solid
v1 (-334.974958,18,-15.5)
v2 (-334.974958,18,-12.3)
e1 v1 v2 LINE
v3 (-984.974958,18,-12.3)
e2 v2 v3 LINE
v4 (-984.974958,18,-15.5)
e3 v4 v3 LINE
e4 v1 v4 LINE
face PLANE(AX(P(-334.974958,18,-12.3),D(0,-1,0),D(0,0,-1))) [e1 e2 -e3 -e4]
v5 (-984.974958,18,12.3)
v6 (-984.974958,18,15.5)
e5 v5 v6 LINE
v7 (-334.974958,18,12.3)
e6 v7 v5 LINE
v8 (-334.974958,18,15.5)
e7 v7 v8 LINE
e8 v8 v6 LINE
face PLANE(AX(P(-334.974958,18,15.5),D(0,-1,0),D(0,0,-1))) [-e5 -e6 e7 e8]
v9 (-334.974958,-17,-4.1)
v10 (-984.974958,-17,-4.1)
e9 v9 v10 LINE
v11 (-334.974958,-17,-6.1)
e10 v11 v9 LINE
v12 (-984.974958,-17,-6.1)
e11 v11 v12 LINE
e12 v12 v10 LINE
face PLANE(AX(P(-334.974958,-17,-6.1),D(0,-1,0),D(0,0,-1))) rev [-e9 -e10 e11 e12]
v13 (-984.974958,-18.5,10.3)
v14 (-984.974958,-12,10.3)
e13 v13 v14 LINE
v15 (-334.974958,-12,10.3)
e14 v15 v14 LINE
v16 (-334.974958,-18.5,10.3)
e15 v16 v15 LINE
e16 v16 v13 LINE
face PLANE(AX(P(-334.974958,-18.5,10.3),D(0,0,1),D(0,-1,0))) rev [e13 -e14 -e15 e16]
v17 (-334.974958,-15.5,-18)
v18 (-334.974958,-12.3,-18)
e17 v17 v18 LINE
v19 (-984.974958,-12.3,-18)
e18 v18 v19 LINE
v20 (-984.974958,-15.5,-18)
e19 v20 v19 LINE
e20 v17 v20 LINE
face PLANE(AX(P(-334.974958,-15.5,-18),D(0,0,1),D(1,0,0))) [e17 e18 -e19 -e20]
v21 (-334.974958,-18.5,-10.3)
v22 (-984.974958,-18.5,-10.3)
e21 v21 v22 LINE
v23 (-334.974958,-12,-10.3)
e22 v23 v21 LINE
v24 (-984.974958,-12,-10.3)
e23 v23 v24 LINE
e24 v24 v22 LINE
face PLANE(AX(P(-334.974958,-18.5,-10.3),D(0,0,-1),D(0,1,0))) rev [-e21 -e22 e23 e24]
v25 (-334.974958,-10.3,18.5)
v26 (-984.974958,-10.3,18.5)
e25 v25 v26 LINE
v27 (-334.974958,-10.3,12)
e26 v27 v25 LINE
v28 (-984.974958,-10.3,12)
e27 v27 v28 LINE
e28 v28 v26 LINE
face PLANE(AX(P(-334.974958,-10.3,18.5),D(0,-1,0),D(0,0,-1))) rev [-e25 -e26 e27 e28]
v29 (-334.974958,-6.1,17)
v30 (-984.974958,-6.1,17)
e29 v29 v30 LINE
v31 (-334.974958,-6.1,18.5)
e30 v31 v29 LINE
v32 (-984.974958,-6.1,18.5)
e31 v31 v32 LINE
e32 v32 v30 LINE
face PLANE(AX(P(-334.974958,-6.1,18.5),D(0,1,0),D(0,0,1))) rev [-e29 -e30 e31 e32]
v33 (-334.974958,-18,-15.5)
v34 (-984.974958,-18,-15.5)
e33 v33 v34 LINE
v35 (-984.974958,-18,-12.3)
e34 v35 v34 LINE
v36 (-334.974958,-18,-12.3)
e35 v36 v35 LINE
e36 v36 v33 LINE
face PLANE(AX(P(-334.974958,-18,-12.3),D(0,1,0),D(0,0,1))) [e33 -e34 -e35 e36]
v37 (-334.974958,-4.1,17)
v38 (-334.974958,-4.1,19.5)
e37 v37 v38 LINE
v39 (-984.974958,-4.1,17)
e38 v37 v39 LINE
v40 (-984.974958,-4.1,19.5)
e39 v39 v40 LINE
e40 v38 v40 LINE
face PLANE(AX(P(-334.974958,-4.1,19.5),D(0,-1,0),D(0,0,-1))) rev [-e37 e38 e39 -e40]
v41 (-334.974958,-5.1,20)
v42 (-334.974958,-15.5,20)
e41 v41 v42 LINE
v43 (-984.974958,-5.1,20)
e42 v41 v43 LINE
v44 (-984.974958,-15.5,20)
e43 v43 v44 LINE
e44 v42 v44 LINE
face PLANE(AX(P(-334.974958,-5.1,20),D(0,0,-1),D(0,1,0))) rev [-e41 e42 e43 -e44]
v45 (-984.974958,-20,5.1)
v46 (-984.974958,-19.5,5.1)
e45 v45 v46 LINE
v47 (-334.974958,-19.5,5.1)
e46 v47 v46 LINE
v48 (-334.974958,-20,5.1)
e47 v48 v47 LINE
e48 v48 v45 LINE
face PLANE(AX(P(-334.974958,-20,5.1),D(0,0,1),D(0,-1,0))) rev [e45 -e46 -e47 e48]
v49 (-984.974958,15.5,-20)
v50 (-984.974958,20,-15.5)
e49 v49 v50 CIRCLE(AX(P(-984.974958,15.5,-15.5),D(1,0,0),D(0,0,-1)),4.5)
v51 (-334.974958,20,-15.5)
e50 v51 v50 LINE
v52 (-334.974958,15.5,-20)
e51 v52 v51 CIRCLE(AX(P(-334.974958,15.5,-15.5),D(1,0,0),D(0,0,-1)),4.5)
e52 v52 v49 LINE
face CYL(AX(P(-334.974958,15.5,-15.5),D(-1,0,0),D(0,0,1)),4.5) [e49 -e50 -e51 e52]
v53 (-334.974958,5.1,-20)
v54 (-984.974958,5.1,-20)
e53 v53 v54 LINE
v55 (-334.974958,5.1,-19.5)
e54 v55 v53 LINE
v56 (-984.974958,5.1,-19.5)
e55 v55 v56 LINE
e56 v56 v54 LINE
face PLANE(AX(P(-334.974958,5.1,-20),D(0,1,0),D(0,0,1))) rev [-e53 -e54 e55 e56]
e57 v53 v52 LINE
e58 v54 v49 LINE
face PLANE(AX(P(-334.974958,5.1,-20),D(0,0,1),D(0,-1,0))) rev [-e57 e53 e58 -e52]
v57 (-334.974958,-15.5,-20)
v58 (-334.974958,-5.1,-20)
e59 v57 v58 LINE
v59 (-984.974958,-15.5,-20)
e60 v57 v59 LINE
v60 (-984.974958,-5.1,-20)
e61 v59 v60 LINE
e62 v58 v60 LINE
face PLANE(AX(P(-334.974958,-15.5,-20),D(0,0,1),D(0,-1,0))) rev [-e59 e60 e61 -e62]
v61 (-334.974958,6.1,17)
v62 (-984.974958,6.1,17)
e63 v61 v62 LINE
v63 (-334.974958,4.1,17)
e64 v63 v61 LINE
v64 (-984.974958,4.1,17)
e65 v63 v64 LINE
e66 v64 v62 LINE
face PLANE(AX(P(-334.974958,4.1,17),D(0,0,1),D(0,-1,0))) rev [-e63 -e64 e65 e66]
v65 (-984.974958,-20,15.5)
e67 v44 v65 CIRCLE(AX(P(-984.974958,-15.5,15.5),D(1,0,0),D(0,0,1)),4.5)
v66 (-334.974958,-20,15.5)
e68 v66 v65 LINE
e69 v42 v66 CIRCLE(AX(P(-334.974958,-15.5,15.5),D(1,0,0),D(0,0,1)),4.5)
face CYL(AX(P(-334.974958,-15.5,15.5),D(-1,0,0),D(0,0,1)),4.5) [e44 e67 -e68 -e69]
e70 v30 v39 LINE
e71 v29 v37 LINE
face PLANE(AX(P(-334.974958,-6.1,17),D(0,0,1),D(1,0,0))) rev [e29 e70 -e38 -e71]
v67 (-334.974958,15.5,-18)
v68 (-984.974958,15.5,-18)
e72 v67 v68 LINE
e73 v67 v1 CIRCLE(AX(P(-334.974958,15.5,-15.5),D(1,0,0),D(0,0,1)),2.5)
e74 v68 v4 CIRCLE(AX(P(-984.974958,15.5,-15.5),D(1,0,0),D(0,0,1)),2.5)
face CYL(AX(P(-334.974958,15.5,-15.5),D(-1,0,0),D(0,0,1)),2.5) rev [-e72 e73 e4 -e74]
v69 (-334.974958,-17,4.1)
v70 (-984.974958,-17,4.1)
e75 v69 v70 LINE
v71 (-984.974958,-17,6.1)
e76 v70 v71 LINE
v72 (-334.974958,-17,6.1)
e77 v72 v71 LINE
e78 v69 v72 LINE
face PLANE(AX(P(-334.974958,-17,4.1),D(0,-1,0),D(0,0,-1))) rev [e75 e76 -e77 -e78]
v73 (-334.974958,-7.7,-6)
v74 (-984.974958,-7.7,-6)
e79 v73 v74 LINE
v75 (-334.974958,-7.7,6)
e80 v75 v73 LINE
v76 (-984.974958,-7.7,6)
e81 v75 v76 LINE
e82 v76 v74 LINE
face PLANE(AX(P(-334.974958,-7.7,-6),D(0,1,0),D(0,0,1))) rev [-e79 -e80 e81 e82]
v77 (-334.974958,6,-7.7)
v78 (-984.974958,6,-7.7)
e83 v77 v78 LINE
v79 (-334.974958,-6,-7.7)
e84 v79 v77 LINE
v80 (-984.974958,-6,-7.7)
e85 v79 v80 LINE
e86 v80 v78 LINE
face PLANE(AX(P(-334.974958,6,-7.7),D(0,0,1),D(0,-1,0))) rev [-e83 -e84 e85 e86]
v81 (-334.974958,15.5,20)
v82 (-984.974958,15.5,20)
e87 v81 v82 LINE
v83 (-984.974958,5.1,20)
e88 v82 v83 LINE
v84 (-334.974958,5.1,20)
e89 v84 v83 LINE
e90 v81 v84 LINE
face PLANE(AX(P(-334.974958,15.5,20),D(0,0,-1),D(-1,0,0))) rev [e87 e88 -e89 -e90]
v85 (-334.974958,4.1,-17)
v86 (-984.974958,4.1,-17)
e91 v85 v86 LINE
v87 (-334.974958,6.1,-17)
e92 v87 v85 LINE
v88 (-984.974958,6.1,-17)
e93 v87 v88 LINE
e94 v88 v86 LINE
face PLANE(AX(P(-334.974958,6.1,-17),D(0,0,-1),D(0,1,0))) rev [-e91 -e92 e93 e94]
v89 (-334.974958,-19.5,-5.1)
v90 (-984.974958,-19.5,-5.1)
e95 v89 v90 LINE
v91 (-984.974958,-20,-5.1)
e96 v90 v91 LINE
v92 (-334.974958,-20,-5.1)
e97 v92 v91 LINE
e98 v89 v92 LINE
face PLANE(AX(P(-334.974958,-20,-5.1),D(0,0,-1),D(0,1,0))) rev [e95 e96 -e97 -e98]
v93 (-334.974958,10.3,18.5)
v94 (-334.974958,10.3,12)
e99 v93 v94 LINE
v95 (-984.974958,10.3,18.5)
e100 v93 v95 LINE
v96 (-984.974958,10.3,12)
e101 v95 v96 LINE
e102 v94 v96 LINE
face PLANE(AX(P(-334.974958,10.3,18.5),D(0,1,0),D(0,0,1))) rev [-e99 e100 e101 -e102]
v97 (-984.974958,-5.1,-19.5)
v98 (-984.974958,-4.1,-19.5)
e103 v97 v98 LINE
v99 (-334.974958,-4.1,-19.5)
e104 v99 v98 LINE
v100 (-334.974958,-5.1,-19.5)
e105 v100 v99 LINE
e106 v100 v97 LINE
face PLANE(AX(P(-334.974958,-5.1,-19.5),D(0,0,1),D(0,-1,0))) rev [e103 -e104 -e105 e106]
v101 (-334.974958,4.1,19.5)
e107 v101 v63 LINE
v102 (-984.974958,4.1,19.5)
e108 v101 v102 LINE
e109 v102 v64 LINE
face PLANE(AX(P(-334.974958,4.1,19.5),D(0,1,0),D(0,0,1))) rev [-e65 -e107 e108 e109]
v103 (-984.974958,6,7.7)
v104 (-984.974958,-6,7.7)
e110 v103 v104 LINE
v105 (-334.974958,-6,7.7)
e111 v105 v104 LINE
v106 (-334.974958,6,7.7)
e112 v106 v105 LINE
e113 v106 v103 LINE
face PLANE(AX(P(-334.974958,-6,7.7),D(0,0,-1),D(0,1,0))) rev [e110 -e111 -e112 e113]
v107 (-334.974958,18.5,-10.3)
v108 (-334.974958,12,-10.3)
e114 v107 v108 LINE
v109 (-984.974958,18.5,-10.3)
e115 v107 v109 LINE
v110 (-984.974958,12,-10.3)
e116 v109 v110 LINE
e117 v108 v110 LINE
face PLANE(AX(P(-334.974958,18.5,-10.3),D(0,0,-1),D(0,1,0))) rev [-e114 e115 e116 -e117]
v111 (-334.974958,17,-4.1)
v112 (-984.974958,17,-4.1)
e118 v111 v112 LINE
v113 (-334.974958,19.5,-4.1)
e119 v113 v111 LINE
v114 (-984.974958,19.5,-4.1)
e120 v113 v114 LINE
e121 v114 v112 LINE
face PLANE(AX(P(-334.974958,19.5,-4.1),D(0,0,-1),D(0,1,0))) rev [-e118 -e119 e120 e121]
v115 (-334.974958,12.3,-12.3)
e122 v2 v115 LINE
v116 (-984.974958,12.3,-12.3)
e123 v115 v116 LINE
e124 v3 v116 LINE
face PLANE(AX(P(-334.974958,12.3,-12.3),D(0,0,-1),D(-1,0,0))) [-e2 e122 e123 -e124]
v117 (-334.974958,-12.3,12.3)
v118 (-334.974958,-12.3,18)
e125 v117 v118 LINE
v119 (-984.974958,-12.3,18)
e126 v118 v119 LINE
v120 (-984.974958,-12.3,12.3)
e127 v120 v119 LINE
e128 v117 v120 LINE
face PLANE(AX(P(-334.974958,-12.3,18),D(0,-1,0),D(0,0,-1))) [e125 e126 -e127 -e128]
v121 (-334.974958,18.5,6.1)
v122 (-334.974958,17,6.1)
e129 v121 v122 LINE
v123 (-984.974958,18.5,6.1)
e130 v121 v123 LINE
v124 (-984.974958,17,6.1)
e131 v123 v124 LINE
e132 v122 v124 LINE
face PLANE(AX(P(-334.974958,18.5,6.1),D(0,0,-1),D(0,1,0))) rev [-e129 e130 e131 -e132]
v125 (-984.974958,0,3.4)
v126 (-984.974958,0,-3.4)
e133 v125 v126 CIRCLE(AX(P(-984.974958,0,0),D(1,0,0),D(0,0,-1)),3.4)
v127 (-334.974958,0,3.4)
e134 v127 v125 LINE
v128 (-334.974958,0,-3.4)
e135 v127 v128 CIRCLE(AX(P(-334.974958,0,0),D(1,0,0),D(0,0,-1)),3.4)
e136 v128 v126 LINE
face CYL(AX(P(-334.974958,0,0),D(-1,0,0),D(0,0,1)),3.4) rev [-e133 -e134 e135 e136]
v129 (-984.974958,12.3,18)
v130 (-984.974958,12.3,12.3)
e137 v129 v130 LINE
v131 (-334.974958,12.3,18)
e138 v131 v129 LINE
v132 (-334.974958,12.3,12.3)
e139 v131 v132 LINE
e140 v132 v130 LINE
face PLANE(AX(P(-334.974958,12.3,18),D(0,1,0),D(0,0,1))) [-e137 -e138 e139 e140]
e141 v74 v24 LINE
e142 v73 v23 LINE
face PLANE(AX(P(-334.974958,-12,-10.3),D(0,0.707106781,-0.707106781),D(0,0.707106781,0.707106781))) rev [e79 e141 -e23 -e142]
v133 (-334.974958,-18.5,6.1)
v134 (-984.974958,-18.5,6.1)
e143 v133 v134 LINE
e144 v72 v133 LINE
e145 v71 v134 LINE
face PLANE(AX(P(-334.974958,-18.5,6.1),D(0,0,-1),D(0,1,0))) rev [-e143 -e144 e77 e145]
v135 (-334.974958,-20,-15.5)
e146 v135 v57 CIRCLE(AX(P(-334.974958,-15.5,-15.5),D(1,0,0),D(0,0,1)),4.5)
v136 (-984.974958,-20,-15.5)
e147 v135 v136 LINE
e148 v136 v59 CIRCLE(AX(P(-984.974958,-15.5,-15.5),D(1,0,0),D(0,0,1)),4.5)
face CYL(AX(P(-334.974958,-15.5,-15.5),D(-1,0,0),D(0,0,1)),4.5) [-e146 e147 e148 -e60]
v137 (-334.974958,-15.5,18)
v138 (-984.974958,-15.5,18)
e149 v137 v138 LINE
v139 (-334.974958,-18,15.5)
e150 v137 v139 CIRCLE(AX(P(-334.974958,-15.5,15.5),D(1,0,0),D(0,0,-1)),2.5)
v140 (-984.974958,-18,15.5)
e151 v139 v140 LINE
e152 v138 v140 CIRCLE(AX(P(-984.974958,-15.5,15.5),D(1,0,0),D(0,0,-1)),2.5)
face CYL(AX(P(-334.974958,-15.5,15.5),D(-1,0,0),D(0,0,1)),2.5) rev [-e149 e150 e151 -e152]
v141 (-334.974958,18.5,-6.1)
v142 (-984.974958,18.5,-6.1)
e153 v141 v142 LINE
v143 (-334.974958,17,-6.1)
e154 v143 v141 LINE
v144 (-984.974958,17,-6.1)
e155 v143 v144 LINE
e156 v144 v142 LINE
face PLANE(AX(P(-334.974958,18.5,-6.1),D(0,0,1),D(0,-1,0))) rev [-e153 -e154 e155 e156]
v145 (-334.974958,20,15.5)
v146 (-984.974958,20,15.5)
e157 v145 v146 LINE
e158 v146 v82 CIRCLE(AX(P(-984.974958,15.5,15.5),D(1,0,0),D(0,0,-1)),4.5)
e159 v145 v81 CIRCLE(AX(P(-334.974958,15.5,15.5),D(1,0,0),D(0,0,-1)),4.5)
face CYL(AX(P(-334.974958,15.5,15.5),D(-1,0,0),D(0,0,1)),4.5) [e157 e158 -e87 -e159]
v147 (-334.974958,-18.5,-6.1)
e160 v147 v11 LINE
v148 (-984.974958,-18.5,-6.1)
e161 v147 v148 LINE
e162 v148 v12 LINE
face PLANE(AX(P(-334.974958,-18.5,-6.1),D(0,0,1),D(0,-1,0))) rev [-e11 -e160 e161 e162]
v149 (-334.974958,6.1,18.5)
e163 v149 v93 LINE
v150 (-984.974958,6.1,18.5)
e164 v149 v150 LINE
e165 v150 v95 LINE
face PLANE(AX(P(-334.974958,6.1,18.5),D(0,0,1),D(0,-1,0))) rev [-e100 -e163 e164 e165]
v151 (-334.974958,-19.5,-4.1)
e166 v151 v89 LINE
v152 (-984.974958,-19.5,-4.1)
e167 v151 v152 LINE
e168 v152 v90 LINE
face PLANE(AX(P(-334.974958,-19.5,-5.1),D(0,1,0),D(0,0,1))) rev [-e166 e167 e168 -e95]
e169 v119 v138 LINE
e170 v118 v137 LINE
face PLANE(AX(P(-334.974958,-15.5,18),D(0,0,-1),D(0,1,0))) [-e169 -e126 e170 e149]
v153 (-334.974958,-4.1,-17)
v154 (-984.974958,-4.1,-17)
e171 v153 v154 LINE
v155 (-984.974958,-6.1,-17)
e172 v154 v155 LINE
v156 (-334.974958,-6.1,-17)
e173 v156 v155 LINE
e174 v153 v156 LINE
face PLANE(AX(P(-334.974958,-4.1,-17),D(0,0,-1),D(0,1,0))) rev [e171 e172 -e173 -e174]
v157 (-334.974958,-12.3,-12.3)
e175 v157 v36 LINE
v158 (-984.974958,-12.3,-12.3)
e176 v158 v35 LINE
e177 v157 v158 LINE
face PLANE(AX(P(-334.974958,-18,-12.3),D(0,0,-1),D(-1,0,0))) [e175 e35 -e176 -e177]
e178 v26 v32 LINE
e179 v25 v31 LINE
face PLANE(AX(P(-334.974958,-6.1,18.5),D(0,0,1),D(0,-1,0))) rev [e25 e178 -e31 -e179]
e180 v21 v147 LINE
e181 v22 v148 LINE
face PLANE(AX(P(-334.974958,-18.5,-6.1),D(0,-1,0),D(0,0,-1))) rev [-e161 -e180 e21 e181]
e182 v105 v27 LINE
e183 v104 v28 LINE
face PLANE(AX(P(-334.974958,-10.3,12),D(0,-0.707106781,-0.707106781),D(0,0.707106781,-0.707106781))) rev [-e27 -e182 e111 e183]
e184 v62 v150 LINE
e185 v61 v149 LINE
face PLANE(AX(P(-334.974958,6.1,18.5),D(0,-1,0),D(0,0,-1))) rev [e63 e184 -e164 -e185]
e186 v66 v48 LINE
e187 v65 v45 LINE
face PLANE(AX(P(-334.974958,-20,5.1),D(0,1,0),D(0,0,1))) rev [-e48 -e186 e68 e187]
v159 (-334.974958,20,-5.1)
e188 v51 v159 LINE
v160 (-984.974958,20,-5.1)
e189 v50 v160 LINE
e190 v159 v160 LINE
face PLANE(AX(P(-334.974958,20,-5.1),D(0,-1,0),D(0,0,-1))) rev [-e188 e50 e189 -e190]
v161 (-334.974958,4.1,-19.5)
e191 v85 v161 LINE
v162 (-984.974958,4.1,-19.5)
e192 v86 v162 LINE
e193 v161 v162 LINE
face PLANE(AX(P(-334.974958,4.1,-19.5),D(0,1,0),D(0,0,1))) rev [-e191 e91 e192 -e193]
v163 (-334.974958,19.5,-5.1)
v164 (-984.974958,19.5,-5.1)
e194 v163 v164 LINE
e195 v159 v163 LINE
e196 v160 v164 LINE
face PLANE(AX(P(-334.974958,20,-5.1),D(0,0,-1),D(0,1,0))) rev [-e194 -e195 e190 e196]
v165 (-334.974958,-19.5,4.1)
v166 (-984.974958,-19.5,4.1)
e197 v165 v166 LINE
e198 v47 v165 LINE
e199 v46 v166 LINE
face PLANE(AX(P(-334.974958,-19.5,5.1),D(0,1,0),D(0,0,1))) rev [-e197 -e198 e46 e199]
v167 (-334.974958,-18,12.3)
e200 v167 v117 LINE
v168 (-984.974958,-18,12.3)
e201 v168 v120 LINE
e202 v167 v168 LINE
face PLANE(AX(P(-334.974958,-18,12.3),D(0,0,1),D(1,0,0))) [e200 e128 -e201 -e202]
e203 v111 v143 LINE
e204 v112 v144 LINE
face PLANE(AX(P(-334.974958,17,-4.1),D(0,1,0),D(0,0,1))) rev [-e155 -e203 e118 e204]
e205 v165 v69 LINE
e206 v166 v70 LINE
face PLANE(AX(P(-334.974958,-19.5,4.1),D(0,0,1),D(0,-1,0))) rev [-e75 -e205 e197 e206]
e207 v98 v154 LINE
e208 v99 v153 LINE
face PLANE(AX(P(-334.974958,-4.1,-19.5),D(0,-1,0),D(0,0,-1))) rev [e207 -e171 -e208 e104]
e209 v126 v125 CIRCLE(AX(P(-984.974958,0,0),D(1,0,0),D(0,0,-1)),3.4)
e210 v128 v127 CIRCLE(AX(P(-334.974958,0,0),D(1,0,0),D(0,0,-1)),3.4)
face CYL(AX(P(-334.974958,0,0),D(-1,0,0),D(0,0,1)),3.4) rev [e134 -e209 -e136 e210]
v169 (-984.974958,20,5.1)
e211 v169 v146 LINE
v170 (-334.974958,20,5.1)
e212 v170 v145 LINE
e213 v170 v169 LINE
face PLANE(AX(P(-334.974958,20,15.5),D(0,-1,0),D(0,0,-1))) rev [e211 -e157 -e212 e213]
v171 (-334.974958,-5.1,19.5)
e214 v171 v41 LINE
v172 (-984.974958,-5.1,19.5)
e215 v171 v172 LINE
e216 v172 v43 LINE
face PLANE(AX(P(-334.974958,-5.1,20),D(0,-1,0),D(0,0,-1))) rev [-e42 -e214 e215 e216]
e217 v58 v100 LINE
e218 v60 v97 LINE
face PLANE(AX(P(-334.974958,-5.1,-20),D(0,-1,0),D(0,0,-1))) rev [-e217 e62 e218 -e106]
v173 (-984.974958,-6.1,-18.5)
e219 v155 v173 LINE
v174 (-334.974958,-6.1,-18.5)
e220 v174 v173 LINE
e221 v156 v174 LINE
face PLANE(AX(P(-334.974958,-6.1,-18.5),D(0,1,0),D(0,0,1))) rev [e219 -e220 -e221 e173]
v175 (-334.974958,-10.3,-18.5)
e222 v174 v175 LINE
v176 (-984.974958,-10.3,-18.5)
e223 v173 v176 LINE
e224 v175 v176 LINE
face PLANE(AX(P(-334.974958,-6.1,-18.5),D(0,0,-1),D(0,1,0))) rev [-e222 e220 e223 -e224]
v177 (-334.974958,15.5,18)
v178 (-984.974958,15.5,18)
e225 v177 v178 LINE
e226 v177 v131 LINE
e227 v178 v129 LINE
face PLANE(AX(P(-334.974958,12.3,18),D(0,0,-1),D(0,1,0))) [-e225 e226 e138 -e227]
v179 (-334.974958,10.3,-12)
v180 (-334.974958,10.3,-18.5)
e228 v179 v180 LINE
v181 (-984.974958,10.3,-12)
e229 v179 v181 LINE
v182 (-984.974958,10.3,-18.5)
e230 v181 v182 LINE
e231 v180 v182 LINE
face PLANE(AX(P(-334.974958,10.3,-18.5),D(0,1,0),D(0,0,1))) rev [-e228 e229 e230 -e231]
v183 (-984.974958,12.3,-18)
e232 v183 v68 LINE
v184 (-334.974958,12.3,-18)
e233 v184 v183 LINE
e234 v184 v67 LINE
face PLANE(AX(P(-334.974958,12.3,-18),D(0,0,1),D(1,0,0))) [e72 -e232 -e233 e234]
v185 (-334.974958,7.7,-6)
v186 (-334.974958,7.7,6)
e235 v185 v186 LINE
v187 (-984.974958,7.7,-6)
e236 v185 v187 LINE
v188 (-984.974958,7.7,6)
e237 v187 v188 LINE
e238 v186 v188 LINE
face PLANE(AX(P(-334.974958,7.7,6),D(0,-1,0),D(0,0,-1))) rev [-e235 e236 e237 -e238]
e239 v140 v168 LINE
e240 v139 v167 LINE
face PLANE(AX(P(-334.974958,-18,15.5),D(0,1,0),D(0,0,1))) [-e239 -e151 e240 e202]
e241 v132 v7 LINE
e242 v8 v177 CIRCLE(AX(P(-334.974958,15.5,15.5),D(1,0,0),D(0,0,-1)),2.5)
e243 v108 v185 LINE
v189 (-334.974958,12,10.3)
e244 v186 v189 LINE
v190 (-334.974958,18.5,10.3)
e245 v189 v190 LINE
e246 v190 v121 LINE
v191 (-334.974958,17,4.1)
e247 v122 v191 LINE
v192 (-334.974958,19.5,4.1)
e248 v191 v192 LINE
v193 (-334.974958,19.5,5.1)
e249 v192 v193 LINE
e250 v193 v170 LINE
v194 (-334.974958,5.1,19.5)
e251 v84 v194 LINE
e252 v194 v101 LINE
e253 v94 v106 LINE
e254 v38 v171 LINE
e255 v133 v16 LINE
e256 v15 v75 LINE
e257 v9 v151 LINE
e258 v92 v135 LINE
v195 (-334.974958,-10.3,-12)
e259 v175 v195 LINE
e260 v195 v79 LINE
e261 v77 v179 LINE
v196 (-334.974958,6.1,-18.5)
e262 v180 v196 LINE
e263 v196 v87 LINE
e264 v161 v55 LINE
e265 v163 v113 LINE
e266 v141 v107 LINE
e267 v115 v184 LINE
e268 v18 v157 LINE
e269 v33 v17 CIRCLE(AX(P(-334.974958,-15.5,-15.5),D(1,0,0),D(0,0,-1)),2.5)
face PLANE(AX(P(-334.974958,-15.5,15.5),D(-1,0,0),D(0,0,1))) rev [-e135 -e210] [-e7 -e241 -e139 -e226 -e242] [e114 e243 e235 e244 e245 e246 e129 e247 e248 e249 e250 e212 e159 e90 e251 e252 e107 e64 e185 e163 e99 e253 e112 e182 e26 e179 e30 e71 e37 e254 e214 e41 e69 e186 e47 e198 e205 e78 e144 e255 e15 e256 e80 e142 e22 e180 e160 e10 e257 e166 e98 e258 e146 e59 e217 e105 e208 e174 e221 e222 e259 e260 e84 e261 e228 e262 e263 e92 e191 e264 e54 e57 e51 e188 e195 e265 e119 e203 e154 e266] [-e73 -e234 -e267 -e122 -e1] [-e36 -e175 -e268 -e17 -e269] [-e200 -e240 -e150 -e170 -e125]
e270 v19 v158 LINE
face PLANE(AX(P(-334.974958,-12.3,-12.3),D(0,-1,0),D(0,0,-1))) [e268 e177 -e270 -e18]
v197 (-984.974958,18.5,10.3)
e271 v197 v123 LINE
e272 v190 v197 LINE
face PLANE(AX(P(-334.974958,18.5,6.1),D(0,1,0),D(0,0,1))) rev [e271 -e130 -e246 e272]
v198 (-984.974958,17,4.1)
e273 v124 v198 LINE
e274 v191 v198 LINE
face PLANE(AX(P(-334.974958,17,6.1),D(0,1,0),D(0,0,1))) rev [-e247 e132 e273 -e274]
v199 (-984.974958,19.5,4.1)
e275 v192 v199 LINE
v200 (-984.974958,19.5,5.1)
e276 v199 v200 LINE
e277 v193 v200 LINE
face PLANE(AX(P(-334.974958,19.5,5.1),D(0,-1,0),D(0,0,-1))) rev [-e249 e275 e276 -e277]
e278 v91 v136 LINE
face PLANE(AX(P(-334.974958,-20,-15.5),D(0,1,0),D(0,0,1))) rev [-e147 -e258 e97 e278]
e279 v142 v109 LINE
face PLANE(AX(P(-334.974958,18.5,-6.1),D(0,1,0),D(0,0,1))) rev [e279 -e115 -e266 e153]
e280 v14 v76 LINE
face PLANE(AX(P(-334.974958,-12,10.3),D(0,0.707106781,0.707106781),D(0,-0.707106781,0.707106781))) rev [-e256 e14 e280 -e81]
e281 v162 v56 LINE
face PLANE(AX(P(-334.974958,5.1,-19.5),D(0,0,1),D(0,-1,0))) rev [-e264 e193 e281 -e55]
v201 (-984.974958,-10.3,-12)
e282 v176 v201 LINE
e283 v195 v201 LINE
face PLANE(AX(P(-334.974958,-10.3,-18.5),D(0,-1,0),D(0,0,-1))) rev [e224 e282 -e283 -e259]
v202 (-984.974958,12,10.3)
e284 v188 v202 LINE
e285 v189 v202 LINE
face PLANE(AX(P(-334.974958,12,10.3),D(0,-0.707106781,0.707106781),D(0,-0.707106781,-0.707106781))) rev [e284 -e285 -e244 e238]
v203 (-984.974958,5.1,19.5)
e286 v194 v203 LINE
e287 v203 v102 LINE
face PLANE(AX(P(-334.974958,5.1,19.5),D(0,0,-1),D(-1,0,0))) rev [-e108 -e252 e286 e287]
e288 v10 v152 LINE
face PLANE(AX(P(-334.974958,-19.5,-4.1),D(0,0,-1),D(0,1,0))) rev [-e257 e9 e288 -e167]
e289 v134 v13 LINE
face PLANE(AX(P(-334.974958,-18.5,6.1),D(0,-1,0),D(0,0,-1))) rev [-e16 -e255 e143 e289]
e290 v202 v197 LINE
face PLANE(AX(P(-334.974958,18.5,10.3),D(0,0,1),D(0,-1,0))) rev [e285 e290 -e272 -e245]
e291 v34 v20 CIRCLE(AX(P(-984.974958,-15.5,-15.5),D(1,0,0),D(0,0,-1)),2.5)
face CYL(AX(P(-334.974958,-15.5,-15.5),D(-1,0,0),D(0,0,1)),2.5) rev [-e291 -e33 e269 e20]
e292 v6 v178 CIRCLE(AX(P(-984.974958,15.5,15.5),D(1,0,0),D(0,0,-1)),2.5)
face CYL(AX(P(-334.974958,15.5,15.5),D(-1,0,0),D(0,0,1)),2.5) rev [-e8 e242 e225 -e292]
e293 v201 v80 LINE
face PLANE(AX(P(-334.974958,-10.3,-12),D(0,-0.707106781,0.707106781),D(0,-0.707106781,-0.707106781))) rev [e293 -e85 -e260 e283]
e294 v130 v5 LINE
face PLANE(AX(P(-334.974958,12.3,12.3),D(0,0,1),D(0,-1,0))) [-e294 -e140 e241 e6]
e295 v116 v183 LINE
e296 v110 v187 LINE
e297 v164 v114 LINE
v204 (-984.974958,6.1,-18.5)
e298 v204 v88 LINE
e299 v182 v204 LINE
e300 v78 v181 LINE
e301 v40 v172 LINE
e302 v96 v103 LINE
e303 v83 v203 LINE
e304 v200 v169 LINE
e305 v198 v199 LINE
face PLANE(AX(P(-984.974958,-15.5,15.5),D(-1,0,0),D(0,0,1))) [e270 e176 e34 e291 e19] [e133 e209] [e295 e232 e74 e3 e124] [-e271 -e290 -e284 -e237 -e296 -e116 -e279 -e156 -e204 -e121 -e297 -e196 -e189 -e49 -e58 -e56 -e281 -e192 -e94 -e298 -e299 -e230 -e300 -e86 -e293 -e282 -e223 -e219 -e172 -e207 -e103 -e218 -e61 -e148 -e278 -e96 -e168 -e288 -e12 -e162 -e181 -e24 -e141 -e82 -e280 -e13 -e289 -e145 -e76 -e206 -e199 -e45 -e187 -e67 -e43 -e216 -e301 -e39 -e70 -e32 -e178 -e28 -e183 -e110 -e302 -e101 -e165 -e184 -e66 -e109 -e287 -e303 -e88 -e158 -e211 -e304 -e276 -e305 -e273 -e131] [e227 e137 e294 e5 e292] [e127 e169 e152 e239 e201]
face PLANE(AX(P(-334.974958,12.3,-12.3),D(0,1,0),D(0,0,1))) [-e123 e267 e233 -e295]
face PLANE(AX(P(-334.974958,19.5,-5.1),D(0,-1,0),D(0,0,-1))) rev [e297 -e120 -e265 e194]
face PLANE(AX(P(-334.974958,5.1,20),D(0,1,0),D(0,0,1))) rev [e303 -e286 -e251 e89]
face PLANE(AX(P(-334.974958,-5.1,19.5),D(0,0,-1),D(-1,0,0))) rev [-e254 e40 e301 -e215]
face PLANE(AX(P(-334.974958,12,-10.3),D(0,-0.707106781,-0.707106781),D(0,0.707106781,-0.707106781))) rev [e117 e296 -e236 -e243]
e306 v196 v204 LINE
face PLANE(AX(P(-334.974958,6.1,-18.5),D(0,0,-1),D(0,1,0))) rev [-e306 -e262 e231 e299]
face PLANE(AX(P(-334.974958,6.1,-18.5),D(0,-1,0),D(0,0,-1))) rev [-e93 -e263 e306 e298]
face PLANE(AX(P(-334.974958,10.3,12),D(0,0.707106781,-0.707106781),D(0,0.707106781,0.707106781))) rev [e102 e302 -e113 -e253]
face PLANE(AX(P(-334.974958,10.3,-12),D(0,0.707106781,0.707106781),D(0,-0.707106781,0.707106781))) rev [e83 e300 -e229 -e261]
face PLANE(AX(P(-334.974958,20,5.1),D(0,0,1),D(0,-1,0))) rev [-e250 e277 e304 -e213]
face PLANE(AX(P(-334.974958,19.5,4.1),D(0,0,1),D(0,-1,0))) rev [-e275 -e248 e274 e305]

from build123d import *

# Parameters (mm, degrees)
SKETCH1_R                                 = 3.4
ALUMINIUM_PROFILE_40_X_40B_X_R4_5_1_DEPTH = 650


with BuildPart() as part:
    # Sketch1 → Aluminium profile 40 X 40B X R4.5(1) (new body)
    with BuildSketch(Plane.YZ.offset(-984.974958264)):
        with BuildLine():
            Line((-5.1, 20), (-5.1, 19.5))
            Line((-5.1, 19.5), (-4.1, 19.5))
            Line((-4.1, 19.5), (-4.1, 17))
            Line((-4.1, 17), (-6.1, 17))
            Line((-6.1, 17), (-6.1, 18.5))
            Line((-6.1, 18.5), (-10.3, 18.5))
            Line((-10.3, 18.5), (-10.3, 12))
            Line((-10.3, 12), (-6, 7.7))
            Line((-6, 7.7), (6, 7.7))
            Line((6, 7.7), (10.3, 12))
            Line((10.3, 12), (10.3, 18.5))
            Line((10.3, 18.5), (6.1, 18.5))
            Line((6.1, 18.5), (6.1, 17))
            Line((6.1, 17), (4.1, 17))
            Line((4.1, 17), (4.1, 19.5))
            Line((4.1, 19.5), (5.1, 19.5))
            Line((5.1, 19.5), (5.1, 20))
            Line((5.1, 20), (15.5, 20))
            ThreePointArc((15.5, 20), (18.681980515, 18.681980515), (20, 15.5))
            Line((20, 15.5), (20, 5.1))
            Line((20, 5.1), (19.5, 5.1))
            Line((19.5, 5.1), (19.5, 4.1))
            Line((19.5, 4.1), (17, 4.1))
            Line((17, 4.1), (17, 6.1))
            Line((17, 6.1), (18.5, 6.1))
            Line((18.5, 6.1), (18.5, 10.3))
            Line((18.5, 10.3), (12, 10.3))
            Line((12, 10.3), (7.7, 6))
            Line((7.7, 6), (7.7, -6))
            Line((7.7, -6), (12, -10.3))
            Line((12, -10.3), (18.5, -10.3))
            Line((18.5, -10.3), (18.5, -6.1))
            Line((18.5, -6.1), (17, -6.1))
            Line((17, -6.1), (17, -4.1))
            Line((17, -4.1), (19.5, -4.1))
            Line((19.5, -4.1), (19.5, -5.1))
            Line((19.5, -5.1), (20, -5.1))
            Line((20, -5.1), (20, -15.5))
            ThreePointArc((20, -15.5), (18.681980515, -18.681980515), (15.5, -20))
            Line((15.5, -20), (5.1, -20))
            Line((5.1, -20), (5.1, -19.5))
            Line((5.1, -19.5), (4.1, -19.5))
            Line((4.1, -19.5), (4.1, -17))
            Line((4.1, -17), (6.1, -17))
            Line((6.1, -17), (6.1, -18.5))
            Line((6.1, -18.5), (10.3, -18.5))
            Line((10.3, -18.5), (10.3, -12))
            Line((10.3, -12), (6, -7.7))
            Line((6, -7.7), (-6, -7.7))
            Line((-6, -7.7), (-10.3, -12))
            Line((-10.3, -12), (-10.3, -18.5))
            Line((-10.3, -18.5), (-6.1, -18.5))
            Line((-6.1, -18.5), (-6.1, -17))
            Line((-6.1, -17), (-4.1, -17))
            Line((-4.1, -17), (-4.1, -19.5))
            Line((-4.1, -19.5), (-5.1, -19.5))
            Line((-5.1, -19.5), (-5.1, -20))
            Line((-5.1, -20), (-15.5, -20))
            ThreePointArc((-15.5, -20), (-18.681980515, -18.681980515), (-20, -15.5))
            Line((-20, -15.5), (-20, -5.1))
            Line((-20, -5.1), (-19.5, -5.1))
            Line((-19.5, -5.1), (-19.5, -4.1))
            Line((-19.5, -4.1), (-17, -4.1))
            Line((-17, -4.1), (-17, -6.1))
            Line((-17, -6.1), (-18.5, -6.1))
            Line((-18.5, -6.1), (-18.5, -10.3))
            Line((-18.5, -10.3), (-12, -10.3))
            Line((-12, -10.3), (-7.7, -6))
            Line((-7.7, -6), (-7.7, 6))
            Line((-7.7, 6), (-12, 10.3))
            Line((-12, 10.3), (-18.5, 10.3))
            Line((-18.5, 10.3), (-18.5, 6.1))
            Line((-18.5, 6.1), (-17, 6.1))
            Line((-17, 6.1), (-17, 4.1))
            Line((-17, 4.1), (-19.5, 4.1))
            Line((-19.5, 4.1), (-19.5, 5.1))
            Line((-19.5, 5.1), (-20, 5.1))
            Line((-20, 5.1), (-20, 15.5))
            ThreePointArc((-20, 15.5), (-18.681980515, 18.681980515), (-15.5, 20))
            Line((-15.5, 20), (-5.1, 20))
        make_face()
        Circle(SKETCH1_R, mode=Mode.SUBTRACT)
        with BuildLine():
            Line((12.3, 18), (15.5, 18))
            ThreePointArc((15.5, 18), (17.267766953, 17.267766953), (18, 15.5))
            Line((18, 15.5), (18, 12.3))
            Line((18, 12.3), (12.3, 12.3))
            Line((12.3, 12.3), (12.3, 18))
        make_face(mode=Mode.SUBTRACT)
        with BuildLine():
            Line((-15.5, 18), (-12.3, 18))
            Line((-12.3, 18), (-12.3, 12.3))
            Line((-12.3, 12.3), (-18, 12.3))
            Line((-18, 12.3), (-18, 15.5))
            ThreePointArc((-18, 15.5), (-17.267766953, 17.267766953), (-15.5, 18))
        make_face(mode=Mode.SUBTRACT)
        with BuildLine():
            Line((-18, -12.3), (-12.3, -12.3))
            Line((-12.3, -12.3), (-12.3, -18))
            Line((-12.3, -18), (-15.5, -18))
            ThreePointArc((-15.5, -18), (-17.267766953, -17.267766953), (-18, -15.5))
            Line((-18, -15.5), (-18, -12.3))
        make_face(mode=Mode.SUBTRACT)
        with BuildLine():
            Line((12.3, -12.3), (18, -12.3))
            Line((18, -12.3), (18, -15.5))
            ThreePointArc((18, -15.5), (17.267766953, -17.267766953), (15.5, -18))
            Line((15.5, -18), (12.3, -18))
            Line((12.3, -18), (12.3, -12.3))
        make_face(mode=Mode.SUBTRACT)
    extrude(amount=ALUMINIUM_PROFILE_40_X_40B_X_R4_5_1_DEPTH)


solid = part.part
